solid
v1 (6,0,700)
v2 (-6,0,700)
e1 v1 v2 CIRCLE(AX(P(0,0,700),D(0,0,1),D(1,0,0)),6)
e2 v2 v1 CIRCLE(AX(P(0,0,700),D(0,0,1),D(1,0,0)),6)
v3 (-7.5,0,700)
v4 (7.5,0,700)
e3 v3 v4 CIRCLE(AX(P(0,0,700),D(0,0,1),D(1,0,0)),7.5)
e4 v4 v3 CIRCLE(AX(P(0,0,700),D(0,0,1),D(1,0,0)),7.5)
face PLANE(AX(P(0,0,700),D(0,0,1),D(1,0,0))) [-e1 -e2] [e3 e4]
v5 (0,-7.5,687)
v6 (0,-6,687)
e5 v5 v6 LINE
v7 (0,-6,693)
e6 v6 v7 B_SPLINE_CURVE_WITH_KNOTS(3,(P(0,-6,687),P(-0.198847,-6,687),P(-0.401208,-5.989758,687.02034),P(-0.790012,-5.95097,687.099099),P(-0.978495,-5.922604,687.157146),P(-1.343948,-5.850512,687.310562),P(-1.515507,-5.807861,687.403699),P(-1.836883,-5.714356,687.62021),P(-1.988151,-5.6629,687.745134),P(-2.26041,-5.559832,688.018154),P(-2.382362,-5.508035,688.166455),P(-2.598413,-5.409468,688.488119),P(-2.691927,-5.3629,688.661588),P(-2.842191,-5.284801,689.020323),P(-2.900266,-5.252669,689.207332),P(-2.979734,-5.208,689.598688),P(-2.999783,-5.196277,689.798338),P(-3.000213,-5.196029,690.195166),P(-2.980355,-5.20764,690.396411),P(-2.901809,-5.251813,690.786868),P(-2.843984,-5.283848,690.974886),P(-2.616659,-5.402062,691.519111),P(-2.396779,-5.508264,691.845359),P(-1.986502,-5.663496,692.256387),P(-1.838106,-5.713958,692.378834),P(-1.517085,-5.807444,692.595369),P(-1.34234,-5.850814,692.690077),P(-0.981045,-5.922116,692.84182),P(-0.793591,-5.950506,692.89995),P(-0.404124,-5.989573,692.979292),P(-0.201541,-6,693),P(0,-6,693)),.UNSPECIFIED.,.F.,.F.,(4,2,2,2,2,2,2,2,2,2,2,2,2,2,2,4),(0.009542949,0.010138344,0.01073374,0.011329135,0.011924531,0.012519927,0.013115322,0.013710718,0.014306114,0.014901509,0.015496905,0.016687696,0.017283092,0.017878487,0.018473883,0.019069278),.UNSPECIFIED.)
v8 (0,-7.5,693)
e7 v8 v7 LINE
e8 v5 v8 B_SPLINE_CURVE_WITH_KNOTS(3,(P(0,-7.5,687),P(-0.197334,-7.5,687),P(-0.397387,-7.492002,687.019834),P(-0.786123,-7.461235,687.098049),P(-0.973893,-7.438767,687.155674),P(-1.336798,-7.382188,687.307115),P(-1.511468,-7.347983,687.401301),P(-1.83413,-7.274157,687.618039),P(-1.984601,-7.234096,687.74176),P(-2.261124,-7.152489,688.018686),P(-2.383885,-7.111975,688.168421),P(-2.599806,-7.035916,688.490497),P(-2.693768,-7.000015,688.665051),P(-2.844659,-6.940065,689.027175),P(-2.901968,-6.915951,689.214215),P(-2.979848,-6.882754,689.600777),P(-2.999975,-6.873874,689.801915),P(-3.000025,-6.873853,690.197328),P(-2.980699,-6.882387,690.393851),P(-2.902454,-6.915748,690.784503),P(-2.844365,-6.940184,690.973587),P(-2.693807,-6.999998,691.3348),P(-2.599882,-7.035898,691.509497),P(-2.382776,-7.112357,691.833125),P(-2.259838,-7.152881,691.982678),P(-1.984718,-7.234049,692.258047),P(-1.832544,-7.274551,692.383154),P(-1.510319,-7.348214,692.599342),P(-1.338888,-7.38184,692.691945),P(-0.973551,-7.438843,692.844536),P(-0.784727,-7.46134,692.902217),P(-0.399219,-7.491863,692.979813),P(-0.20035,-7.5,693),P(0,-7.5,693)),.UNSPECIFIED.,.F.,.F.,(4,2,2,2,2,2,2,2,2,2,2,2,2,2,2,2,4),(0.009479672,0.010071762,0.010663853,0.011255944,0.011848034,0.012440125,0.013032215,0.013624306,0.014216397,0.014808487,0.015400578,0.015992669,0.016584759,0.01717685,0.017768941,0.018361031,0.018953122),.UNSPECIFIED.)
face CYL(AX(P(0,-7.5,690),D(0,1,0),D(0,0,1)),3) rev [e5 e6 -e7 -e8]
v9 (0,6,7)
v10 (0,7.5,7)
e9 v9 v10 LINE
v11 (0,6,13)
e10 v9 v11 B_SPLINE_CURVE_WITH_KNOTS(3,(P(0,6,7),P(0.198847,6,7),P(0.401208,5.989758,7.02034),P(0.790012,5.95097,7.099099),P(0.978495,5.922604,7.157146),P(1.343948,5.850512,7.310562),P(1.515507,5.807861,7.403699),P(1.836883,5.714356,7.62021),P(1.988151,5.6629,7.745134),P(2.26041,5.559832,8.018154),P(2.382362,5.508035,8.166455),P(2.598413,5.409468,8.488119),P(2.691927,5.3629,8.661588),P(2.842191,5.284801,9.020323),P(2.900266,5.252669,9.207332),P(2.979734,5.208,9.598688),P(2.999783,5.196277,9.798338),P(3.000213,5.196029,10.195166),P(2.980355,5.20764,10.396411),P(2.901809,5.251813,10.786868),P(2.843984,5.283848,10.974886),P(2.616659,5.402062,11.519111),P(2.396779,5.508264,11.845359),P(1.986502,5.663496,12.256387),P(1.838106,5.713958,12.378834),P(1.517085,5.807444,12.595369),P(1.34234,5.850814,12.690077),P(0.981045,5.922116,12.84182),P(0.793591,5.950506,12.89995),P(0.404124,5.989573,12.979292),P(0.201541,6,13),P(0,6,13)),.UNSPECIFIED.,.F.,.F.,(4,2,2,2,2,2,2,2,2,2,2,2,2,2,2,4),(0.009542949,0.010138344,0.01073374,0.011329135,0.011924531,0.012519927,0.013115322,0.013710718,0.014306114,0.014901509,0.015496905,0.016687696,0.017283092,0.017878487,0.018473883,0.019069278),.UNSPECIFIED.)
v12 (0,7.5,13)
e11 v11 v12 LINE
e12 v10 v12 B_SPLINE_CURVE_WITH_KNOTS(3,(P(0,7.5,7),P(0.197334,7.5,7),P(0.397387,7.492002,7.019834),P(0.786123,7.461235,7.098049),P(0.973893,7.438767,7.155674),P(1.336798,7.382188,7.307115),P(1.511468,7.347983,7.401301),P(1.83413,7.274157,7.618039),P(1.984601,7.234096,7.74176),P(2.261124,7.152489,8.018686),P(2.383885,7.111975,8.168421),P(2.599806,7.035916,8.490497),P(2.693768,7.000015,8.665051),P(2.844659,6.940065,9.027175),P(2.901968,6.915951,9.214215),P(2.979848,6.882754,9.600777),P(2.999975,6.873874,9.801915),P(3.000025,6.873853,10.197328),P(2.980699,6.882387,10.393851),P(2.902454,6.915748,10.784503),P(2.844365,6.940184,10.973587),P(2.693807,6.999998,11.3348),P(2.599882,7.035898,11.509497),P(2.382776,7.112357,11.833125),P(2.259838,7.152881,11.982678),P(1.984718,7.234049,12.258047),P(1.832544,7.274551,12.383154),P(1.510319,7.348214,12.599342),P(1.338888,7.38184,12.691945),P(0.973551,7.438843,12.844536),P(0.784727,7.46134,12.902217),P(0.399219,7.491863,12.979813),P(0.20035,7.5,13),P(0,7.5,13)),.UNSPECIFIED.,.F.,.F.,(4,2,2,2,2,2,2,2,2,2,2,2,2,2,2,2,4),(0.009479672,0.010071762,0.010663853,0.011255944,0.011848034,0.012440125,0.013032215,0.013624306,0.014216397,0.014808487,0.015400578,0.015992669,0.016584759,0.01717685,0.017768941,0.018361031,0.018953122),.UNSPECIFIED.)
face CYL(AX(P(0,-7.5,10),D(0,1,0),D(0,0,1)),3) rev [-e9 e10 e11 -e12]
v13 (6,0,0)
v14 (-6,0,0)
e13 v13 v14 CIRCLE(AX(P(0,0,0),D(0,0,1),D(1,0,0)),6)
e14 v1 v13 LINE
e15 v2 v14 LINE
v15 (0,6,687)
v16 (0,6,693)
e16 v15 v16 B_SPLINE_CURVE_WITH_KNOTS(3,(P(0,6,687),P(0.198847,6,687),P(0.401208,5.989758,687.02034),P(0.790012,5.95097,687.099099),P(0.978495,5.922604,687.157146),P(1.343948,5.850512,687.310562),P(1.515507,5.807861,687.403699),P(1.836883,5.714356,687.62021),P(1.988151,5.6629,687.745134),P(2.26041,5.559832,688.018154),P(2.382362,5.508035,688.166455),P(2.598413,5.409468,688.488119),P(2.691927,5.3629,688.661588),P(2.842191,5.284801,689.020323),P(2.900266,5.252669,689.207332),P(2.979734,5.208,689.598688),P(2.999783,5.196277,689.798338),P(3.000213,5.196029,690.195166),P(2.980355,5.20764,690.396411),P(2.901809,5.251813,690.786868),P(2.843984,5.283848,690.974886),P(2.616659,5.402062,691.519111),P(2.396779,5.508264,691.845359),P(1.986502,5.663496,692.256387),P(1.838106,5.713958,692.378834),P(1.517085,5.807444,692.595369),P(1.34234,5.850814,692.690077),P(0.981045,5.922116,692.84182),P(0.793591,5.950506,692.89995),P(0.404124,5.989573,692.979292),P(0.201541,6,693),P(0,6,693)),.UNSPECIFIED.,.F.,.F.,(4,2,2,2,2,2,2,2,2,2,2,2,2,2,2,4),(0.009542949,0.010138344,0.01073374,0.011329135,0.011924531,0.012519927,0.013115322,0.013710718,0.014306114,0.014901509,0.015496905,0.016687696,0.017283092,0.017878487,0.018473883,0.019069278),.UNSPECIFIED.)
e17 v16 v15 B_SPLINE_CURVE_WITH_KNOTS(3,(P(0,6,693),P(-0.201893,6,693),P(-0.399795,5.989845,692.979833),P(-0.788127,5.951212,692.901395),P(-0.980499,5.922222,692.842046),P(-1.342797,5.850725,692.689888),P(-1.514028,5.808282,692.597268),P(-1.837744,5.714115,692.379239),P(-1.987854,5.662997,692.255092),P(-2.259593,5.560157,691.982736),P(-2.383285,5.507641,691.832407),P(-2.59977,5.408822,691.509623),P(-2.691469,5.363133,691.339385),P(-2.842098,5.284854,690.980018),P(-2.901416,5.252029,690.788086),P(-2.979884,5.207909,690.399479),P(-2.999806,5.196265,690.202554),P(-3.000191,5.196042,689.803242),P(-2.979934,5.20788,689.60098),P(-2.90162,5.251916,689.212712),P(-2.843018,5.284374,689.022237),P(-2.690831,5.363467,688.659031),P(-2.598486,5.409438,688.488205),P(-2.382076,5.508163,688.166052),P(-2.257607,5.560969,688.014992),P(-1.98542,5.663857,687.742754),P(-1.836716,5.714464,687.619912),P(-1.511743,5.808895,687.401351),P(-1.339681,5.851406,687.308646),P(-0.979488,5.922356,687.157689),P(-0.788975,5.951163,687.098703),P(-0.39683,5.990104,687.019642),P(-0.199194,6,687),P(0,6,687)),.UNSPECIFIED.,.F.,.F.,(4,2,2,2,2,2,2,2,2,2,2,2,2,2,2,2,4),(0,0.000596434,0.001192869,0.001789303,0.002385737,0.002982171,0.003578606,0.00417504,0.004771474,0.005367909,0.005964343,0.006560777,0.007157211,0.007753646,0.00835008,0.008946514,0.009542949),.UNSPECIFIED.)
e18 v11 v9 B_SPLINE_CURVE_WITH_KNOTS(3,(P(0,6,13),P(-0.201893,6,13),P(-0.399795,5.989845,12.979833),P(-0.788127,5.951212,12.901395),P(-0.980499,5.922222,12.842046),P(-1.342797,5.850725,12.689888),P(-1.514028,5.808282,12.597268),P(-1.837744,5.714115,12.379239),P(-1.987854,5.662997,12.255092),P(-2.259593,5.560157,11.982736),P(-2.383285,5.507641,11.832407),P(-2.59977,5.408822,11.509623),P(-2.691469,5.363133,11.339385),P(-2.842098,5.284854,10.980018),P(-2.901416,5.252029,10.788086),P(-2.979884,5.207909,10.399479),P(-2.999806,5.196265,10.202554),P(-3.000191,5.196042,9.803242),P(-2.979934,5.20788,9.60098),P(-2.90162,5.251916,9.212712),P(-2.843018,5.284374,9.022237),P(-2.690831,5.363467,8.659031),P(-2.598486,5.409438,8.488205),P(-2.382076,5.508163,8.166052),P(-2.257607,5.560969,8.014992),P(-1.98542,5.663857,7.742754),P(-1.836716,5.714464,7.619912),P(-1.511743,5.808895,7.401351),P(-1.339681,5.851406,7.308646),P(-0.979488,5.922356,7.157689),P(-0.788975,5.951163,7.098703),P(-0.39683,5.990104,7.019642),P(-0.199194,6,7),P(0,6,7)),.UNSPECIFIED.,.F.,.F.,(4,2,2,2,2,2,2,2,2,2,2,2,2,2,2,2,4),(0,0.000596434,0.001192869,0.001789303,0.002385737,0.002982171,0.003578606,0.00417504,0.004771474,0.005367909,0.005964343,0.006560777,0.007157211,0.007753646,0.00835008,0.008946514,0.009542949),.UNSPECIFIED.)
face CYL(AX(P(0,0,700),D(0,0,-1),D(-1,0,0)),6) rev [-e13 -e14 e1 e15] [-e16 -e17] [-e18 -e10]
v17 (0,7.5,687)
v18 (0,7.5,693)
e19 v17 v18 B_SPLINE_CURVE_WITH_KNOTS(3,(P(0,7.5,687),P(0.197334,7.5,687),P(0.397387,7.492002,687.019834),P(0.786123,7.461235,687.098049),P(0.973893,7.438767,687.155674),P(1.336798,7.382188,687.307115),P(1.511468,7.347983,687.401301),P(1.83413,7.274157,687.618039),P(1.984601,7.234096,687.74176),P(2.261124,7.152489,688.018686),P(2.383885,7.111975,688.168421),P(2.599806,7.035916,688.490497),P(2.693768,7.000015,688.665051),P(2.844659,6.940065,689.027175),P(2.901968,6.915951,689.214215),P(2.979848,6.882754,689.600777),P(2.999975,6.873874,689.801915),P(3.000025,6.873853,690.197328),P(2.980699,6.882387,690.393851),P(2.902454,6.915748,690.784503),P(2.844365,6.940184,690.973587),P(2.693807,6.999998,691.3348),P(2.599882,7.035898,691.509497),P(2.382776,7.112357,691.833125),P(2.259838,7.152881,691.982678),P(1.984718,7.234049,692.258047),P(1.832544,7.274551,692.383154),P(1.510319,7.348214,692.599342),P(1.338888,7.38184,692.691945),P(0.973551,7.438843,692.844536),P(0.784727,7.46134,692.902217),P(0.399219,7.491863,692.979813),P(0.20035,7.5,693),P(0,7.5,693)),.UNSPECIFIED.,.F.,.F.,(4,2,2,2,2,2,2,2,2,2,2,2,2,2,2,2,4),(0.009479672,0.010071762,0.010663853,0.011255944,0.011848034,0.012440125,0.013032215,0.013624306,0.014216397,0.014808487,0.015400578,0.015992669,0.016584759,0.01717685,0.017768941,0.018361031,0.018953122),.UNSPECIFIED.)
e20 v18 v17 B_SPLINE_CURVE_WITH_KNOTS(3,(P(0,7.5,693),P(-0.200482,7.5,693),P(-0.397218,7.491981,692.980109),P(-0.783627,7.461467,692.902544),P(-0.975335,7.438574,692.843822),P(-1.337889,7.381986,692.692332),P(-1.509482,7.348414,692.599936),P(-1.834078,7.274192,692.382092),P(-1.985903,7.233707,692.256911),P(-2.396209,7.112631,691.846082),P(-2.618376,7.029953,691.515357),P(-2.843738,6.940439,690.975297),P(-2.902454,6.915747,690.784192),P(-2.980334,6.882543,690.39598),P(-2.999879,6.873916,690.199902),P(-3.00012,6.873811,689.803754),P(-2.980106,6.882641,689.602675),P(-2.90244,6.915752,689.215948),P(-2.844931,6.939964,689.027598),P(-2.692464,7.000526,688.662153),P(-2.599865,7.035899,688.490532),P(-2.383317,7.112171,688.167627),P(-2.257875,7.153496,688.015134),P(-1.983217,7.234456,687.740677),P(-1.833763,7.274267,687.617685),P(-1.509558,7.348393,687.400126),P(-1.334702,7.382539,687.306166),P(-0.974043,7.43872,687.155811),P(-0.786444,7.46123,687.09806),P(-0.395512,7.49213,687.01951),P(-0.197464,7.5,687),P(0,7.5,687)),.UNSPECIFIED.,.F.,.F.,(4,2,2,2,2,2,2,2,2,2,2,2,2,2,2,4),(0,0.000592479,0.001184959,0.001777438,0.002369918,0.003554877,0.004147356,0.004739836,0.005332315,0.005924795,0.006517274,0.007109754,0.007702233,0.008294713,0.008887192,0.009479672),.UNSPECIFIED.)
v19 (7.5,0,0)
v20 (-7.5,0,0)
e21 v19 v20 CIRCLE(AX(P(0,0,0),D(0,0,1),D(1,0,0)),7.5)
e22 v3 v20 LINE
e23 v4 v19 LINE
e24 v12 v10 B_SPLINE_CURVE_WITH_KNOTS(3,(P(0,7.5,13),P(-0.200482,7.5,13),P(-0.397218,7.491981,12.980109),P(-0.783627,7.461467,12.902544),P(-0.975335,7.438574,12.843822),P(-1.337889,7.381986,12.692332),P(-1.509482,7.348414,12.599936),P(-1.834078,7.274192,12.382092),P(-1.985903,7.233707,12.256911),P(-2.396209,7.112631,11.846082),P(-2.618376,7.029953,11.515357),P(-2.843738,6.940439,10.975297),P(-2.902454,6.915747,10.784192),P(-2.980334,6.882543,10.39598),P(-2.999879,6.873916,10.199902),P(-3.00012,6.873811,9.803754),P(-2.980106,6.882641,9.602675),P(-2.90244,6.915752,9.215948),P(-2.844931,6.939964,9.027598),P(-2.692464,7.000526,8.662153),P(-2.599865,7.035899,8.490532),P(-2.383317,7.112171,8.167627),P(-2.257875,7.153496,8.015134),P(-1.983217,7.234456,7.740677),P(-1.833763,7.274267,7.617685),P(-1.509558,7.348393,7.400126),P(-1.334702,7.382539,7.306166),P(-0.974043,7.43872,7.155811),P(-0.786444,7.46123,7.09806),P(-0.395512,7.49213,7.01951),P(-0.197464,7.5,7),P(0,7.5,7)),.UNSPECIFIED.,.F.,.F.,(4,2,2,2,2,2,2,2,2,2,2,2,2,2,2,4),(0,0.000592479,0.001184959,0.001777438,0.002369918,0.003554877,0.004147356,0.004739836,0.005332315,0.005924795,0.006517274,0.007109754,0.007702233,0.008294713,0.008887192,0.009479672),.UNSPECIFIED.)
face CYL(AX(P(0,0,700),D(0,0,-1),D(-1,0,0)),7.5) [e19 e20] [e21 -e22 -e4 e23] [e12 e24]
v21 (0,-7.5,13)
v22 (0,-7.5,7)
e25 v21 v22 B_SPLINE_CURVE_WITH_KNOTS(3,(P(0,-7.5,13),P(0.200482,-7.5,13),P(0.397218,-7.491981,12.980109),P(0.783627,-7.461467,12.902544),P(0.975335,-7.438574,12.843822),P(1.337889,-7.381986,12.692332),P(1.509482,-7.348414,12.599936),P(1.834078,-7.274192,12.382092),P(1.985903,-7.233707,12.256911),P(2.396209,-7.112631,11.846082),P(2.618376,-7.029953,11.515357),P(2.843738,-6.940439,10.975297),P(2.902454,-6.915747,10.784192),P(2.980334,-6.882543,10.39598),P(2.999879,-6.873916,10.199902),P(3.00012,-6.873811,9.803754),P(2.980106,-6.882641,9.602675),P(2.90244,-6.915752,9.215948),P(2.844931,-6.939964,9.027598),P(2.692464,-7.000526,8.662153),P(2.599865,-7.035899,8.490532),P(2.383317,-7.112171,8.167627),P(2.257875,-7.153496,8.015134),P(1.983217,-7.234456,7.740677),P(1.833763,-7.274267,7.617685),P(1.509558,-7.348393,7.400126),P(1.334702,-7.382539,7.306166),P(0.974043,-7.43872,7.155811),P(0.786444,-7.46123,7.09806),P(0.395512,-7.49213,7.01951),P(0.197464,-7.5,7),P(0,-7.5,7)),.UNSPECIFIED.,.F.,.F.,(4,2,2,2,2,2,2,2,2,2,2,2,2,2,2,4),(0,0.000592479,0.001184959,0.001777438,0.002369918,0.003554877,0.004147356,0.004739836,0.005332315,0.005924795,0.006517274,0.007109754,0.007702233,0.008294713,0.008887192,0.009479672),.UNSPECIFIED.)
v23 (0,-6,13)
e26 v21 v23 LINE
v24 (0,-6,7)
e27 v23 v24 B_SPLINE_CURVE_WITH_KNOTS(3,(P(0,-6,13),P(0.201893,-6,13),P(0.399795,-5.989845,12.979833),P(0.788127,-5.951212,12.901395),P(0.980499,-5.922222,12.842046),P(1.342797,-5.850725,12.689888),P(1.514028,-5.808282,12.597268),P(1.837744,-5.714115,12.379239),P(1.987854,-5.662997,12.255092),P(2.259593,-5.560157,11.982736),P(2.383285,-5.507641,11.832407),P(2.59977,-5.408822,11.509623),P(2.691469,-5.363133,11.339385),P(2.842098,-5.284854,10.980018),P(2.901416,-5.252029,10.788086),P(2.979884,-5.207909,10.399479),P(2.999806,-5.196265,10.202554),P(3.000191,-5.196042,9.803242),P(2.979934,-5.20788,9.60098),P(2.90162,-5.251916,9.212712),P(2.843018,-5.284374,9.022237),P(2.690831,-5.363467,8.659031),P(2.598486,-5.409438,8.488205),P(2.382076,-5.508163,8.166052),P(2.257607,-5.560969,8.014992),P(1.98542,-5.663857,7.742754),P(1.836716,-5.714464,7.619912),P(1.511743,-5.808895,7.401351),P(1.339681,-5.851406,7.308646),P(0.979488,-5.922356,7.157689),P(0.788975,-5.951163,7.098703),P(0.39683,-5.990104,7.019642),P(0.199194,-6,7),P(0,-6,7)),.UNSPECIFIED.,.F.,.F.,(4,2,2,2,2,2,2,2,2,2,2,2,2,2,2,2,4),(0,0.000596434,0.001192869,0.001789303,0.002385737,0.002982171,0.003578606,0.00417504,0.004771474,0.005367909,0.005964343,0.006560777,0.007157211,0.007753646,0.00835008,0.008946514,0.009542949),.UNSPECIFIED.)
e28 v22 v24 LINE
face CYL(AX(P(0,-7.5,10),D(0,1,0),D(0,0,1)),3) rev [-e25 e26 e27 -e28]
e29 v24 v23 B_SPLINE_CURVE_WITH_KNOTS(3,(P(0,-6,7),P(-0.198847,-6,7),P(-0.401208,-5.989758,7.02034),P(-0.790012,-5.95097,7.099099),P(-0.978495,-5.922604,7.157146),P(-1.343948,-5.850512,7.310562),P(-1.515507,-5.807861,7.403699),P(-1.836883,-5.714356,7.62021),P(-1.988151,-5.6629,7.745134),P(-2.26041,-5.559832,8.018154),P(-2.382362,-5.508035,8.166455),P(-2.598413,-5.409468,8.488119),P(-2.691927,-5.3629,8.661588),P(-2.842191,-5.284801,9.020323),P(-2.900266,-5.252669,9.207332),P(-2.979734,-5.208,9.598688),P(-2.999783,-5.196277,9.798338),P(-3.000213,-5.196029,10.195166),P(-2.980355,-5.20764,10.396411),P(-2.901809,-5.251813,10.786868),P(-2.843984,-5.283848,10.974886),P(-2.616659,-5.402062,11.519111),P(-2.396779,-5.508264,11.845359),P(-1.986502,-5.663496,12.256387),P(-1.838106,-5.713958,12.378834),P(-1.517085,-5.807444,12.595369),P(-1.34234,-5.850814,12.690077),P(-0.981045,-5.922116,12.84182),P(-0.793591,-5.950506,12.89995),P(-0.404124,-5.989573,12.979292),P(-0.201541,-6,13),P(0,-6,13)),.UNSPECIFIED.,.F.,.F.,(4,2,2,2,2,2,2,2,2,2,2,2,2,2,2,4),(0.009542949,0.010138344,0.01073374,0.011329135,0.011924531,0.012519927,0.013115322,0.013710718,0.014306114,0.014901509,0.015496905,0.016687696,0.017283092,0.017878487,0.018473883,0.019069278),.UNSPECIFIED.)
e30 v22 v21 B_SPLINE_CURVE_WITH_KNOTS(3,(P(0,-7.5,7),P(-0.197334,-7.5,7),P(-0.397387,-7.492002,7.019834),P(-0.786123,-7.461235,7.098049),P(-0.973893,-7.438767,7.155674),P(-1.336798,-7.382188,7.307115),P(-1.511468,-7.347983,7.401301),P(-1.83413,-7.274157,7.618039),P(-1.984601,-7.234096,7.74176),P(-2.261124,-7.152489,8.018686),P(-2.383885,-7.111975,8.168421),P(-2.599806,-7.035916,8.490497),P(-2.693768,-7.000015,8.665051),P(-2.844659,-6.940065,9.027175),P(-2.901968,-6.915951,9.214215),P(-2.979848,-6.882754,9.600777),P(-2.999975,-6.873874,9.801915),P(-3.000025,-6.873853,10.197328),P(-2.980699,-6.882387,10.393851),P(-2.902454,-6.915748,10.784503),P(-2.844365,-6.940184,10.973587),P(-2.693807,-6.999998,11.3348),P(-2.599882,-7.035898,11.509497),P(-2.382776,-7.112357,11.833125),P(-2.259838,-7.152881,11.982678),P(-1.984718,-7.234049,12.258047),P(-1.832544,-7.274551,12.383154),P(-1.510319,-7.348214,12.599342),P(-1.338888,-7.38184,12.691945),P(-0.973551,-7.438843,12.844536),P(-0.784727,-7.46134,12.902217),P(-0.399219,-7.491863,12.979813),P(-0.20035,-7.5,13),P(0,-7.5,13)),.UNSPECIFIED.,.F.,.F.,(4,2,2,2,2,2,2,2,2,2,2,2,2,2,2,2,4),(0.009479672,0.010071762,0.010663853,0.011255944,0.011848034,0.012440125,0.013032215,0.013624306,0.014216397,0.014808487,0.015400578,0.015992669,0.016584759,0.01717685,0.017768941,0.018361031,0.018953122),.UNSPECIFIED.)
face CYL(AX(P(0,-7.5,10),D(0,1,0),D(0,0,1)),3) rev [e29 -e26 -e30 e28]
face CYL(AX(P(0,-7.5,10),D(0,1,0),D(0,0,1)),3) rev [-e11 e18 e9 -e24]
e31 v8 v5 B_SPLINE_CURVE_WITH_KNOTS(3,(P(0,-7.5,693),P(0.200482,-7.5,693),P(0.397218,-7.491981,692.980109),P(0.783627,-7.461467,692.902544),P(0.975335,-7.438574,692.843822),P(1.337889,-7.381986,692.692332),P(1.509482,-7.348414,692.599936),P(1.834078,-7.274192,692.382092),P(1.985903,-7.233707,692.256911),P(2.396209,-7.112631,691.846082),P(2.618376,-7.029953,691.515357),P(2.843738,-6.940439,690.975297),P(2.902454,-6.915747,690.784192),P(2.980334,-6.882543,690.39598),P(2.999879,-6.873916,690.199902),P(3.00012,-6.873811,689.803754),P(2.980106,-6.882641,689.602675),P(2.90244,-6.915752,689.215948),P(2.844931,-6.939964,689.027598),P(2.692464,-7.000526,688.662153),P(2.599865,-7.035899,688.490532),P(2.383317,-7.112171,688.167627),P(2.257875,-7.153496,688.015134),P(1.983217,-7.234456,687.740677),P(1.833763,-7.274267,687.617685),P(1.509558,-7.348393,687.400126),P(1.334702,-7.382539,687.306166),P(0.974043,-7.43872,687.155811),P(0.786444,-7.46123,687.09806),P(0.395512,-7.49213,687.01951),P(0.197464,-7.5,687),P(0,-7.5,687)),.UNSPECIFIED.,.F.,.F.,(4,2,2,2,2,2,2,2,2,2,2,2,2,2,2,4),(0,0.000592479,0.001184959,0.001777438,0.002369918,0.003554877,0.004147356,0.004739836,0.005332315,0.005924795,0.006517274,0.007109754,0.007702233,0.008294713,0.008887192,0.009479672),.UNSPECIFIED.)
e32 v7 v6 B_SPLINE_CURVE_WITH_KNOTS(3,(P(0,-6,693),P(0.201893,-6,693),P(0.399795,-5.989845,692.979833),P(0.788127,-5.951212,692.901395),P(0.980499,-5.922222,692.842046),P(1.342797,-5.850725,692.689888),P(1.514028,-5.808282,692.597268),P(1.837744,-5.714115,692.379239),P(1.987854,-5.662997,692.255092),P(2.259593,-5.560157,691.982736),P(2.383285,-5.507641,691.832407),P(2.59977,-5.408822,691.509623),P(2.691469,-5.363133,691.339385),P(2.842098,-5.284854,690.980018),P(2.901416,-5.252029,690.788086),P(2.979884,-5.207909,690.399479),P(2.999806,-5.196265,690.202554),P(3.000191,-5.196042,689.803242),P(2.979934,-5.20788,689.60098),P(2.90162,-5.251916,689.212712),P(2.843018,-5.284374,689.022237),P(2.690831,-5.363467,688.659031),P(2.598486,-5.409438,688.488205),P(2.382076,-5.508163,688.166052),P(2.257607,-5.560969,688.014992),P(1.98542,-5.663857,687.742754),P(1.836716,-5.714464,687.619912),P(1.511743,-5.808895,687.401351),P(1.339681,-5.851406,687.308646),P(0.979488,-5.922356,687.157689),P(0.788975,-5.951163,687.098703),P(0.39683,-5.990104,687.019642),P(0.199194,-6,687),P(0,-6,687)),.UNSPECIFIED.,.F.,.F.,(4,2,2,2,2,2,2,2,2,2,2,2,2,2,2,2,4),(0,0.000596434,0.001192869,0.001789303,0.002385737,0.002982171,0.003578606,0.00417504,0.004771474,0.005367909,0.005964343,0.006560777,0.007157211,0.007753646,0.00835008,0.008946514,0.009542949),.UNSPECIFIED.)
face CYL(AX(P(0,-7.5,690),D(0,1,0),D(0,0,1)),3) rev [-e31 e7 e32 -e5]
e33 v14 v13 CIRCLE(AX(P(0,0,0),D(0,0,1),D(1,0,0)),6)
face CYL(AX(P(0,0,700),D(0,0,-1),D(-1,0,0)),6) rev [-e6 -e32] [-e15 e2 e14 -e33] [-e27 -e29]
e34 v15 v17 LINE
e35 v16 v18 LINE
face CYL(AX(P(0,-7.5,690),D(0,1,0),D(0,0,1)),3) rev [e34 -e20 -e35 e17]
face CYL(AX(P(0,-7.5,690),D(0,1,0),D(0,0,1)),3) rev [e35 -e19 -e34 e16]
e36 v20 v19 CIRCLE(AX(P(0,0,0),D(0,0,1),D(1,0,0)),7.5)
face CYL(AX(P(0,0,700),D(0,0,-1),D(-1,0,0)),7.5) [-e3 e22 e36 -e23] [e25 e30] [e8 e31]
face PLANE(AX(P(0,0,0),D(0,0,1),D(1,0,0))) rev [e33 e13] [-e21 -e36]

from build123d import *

# Parameters (mm, degrees)
SKETCH1_R               = 7.5
SKETCH1_R_2             = 6
BOSS_EXTRUDE1_DEPTH     = 700
CUT_EXTRUDE1_DEPTH      = 701.080352531
CUT_EXTRUDE1_DEPTH_BACK = 701.080352531
SKETCH2_R               = 3


with BuildPart() as part:
    # Sketch1 → Boss-Extrude1 (new body)
    with BuildSketch(Plane.XY):
        Circle(SKETCH1_R)
        Circle(SKETCH1_R_2, mode=Mode.SUBTRACT)
    extrude(amount=BOSS_EXTRUDE1_DEPTH)

    # Sketch2 → Cut-Extrude1 (cut, two sides: drawn at the far end of the back side and taken through both)
    with BuildSketch(Plane(origin=(0, 0, 0), x_dir=(1, 0, 0), z_dir=(0, 1, 0)).offset(-CUT_EXTRUDE1_DEPTH_BACK)):
        with Locations(Location((0, -10, 0), (0, 0, 270))):
            Circle(SKETCH2_R)
        with Locations(Location((0, -690, 0), (0, 0, 270))):
            Circle(SKETCH2_R)
    extrude(amount=CUT_EXTRUDE1_DEPTH + CUT_EXTRUDE1_DEPTH_BACK, mode=Mode.SUBTRACT)


solid = part.part
